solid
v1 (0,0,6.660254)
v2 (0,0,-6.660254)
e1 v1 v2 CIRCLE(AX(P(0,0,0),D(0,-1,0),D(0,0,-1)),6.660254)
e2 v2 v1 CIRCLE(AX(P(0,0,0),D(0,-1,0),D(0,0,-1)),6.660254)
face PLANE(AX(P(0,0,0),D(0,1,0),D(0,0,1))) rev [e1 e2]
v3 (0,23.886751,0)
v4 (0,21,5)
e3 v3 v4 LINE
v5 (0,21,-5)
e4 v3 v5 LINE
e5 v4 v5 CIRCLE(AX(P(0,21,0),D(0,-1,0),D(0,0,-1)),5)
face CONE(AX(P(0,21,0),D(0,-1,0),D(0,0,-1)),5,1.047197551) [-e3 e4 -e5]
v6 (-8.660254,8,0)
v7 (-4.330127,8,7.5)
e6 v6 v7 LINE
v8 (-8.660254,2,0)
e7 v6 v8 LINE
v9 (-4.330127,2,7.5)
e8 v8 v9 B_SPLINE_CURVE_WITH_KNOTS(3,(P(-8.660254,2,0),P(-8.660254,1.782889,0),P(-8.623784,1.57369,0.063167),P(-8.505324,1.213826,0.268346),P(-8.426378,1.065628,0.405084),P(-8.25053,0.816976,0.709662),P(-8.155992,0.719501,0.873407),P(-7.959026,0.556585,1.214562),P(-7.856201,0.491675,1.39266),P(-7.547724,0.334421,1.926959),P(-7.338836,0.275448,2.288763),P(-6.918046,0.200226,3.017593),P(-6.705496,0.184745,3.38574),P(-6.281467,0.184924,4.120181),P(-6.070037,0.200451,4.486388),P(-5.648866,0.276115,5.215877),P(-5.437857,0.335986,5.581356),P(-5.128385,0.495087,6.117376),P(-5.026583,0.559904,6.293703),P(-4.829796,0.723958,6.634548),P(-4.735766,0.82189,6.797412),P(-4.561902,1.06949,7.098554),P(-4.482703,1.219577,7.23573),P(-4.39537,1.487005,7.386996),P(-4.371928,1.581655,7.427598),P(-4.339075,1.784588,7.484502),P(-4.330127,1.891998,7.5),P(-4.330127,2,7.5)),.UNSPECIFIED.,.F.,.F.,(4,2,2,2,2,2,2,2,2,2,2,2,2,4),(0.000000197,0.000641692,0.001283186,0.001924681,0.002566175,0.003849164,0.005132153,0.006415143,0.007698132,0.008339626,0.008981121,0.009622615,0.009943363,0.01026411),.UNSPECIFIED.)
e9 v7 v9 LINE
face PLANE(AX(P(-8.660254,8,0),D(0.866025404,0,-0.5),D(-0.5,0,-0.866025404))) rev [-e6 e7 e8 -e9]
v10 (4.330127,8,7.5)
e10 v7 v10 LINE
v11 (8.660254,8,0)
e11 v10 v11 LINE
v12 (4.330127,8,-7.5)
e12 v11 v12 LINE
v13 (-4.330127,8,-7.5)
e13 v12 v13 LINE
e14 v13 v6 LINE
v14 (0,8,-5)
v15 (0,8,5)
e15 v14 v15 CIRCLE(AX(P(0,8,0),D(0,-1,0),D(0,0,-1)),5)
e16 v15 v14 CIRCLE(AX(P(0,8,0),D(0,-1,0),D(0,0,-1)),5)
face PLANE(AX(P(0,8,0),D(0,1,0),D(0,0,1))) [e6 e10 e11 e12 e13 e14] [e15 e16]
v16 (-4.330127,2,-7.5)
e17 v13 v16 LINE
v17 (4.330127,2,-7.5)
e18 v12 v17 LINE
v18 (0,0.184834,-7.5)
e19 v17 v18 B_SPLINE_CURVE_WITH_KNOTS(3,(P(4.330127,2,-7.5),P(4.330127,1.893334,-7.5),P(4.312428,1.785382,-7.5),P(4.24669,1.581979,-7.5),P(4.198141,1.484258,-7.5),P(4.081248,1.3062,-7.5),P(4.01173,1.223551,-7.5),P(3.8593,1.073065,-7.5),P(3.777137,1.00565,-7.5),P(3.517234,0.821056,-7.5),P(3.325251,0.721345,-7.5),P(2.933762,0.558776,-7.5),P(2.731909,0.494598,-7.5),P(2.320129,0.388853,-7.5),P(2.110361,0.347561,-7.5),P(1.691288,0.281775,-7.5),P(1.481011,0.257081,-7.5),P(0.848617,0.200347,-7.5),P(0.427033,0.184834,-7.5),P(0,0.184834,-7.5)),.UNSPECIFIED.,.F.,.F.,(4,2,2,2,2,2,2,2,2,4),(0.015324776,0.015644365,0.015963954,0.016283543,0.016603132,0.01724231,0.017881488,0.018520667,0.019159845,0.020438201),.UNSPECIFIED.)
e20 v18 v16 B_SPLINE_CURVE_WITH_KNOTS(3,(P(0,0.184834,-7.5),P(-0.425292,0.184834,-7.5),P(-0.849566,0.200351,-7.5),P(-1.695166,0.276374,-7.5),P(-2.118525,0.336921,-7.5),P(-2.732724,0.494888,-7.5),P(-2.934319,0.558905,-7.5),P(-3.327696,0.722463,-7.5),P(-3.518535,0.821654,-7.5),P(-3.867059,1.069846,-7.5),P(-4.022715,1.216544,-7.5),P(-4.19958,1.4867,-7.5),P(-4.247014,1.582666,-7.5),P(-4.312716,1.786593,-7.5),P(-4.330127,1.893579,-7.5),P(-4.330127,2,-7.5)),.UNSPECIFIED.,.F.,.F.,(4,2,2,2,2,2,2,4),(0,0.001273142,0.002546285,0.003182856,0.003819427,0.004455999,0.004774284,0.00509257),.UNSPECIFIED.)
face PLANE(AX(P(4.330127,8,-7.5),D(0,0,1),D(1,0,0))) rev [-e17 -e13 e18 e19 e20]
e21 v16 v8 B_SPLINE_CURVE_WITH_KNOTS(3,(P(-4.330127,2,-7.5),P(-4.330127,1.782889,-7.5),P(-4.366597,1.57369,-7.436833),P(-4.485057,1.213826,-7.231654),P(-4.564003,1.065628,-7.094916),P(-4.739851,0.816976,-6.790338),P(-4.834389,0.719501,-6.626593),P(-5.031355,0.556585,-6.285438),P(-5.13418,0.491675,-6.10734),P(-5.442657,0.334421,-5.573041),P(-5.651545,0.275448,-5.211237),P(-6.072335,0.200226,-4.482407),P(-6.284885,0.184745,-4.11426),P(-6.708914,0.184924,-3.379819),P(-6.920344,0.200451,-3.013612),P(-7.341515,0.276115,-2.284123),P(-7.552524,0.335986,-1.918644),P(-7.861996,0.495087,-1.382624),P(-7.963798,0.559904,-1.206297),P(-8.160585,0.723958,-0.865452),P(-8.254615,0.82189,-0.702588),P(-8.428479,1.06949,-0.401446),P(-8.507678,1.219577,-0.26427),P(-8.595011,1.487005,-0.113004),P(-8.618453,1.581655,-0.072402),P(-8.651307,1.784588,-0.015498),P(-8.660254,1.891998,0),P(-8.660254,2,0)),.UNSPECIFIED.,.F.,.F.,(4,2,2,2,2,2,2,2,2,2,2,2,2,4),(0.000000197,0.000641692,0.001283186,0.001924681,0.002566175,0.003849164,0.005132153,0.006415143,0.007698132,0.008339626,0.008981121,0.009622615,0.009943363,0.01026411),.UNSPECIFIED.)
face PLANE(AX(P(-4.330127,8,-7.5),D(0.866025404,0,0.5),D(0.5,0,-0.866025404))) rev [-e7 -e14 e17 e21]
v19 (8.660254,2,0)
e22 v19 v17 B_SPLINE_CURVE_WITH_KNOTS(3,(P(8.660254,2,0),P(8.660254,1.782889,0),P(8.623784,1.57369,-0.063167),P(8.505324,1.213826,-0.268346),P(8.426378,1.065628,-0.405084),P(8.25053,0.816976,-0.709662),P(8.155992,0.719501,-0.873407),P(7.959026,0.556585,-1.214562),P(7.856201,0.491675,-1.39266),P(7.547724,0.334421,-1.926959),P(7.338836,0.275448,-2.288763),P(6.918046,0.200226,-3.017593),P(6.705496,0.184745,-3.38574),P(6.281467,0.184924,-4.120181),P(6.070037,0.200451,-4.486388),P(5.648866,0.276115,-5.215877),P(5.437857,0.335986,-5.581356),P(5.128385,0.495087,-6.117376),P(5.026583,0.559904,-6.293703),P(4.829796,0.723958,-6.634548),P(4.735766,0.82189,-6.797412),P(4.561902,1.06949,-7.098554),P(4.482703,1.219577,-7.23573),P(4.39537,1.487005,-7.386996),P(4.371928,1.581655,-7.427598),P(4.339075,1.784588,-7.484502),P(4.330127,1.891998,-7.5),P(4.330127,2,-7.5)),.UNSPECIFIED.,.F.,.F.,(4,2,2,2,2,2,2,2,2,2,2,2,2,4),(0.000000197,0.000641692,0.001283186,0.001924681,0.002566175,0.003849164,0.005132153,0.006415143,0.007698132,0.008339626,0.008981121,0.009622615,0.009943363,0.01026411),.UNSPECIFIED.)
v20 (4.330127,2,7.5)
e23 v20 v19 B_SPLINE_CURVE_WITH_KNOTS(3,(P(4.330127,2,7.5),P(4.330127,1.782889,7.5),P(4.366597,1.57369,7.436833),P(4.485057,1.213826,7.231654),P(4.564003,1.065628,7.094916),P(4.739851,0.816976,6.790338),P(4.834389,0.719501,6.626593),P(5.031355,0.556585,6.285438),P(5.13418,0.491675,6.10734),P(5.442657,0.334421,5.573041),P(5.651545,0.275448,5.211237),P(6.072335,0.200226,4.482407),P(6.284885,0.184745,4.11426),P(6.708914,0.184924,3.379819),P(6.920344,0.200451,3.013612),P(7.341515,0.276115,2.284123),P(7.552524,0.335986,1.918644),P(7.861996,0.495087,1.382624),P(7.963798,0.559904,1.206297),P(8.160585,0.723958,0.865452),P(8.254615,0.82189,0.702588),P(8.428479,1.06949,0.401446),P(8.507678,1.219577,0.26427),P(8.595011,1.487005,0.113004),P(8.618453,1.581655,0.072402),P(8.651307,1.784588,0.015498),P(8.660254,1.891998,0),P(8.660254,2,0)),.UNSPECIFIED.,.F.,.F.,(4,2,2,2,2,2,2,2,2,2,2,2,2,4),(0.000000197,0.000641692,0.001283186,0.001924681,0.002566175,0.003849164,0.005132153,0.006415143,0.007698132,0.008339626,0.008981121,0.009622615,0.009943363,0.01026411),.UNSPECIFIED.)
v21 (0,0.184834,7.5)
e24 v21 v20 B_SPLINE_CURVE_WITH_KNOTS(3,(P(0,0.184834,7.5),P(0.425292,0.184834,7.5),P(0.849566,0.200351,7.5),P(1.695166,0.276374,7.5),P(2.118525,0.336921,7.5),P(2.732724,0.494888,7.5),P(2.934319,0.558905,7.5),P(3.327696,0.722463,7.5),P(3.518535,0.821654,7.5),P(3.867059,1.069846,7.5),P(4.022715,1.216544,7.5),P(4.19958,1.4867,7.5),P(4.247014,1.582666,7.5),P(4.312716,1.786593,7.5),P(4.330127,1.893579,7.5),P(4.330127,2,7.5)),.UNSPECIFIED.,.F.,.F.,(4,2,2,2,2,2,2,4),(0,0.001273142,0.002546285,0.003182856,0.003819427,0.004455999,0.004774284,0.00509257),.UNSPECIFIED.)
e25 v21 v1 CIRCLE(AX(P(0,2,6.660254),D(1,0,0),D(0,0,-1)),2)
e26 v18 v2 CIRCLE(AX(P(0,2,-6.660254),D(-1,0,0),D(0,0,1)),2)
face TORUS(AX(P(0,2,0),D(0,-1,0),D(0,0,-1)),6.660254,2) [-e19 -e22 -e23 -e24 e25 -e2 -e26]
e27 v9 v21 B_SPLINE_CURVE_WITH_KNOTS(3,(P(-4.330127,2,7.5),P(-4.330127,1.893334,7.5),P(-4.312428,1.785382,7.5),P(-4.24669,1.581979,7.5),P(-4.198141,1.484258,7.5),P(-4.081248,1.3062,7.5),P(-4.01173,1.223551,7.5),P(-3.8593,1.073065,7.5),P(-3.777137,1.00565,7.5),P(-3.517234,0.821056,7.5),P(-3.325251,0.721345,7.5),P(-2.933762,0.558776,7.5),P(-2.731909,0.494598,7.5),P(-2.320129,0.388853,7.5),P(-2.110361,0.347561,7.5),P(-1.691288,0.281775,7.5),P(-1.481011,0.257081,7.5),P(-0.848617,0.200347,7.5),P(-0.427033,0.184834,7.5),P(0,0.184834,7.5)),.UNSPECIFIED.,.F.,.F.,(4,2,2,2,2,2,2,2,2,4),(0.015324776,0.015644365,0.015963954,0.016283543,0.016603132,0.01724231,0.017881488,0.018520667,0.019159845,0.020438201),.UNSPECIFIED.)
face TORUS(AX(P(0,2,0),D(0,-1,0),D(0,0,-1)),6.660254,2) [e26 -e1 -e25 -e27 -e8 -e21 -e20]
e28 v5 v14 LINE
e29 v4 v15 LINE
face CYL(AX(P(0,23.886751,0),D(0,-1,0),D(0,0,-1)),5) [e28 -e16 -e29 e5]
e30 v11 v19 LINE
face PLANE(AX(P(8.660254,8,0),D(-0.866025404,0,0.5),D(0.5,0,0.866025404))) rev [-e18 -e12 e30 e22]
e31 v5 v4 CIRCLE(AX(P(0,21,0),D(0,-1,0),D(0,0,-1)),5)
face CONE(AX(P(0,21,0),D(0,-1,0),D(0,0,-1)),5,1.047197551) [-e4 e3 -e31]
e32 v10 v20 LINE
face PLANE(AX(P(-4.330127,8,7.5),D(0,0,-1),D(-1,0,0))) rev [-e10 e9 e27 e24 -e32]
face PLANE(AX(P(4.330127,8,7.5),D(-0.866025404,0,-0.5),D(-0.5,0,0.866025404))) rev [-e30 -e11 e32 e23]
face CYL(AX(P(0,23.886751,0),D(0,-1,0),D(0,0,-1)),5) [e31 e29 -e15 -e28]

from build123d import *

# Parameters (mm, degrees)
HEX_HEAD_15AF_DEPTH = 8


with BuildPart() as part:
    # Hex Head Profile → Hex Head 15AF (new body)
    with BuildSketch(Plane(origin=(0, 0, 0), x_dir=(1, 0, 0), z_dir=(0, 1, 0))):
        Polygon((8.660254038, 0), (4.330127019, 7.5), (-4.330127019, 7.5), (-8.660254038, 0), (-4.330127019, -7.5), (4.330127019, -7.5), align=None)
    extrude(amount=HEX_HEAD_15AF_DEPTH)

    # Shank Profile → Shank with Cone Point (revolve)
    with BuildSketch(Plane.XY, mode=Mode.PRIVATE) as shank_with_cone_point_sk:
        Polygon((0, 8), (0, 23.886751346), (5, 21), (5, 8), align=None)
    revolve(shank_with_cone_point_sk.sketch.rotate(Axis((0, 23.886751346, 0), (0, 1, 0)), 90), axis=Axis((0, 23.886751346, 0), (0, 1, 0)))

    # Head Chamfer Profile → Head Chamfer Cut (revolve, cut)
    with BuildSketch(Plane.XY, mode=Mode.PRIVATE) as head_chamfer_cut_sk:
        with BuildLine():
            Line((8.660254038, 0), (6.660254038, 0))
            ThreePointArc((6.660254038, 0), (8.0744676, 0.585786438), (8.660254038, 2))
            Line((8.660254038, 2), (8.660254038, 0))
        make_face()
    revolve(head_chamfer_cut_sk.sketch.rotate(Axis((0, 0, 0), (0, 1, 0)), 90), axis=Axis((0, 0, 0), (0, 1, 0)), mode=Mode.SUBTRACT)


solid = part.part
